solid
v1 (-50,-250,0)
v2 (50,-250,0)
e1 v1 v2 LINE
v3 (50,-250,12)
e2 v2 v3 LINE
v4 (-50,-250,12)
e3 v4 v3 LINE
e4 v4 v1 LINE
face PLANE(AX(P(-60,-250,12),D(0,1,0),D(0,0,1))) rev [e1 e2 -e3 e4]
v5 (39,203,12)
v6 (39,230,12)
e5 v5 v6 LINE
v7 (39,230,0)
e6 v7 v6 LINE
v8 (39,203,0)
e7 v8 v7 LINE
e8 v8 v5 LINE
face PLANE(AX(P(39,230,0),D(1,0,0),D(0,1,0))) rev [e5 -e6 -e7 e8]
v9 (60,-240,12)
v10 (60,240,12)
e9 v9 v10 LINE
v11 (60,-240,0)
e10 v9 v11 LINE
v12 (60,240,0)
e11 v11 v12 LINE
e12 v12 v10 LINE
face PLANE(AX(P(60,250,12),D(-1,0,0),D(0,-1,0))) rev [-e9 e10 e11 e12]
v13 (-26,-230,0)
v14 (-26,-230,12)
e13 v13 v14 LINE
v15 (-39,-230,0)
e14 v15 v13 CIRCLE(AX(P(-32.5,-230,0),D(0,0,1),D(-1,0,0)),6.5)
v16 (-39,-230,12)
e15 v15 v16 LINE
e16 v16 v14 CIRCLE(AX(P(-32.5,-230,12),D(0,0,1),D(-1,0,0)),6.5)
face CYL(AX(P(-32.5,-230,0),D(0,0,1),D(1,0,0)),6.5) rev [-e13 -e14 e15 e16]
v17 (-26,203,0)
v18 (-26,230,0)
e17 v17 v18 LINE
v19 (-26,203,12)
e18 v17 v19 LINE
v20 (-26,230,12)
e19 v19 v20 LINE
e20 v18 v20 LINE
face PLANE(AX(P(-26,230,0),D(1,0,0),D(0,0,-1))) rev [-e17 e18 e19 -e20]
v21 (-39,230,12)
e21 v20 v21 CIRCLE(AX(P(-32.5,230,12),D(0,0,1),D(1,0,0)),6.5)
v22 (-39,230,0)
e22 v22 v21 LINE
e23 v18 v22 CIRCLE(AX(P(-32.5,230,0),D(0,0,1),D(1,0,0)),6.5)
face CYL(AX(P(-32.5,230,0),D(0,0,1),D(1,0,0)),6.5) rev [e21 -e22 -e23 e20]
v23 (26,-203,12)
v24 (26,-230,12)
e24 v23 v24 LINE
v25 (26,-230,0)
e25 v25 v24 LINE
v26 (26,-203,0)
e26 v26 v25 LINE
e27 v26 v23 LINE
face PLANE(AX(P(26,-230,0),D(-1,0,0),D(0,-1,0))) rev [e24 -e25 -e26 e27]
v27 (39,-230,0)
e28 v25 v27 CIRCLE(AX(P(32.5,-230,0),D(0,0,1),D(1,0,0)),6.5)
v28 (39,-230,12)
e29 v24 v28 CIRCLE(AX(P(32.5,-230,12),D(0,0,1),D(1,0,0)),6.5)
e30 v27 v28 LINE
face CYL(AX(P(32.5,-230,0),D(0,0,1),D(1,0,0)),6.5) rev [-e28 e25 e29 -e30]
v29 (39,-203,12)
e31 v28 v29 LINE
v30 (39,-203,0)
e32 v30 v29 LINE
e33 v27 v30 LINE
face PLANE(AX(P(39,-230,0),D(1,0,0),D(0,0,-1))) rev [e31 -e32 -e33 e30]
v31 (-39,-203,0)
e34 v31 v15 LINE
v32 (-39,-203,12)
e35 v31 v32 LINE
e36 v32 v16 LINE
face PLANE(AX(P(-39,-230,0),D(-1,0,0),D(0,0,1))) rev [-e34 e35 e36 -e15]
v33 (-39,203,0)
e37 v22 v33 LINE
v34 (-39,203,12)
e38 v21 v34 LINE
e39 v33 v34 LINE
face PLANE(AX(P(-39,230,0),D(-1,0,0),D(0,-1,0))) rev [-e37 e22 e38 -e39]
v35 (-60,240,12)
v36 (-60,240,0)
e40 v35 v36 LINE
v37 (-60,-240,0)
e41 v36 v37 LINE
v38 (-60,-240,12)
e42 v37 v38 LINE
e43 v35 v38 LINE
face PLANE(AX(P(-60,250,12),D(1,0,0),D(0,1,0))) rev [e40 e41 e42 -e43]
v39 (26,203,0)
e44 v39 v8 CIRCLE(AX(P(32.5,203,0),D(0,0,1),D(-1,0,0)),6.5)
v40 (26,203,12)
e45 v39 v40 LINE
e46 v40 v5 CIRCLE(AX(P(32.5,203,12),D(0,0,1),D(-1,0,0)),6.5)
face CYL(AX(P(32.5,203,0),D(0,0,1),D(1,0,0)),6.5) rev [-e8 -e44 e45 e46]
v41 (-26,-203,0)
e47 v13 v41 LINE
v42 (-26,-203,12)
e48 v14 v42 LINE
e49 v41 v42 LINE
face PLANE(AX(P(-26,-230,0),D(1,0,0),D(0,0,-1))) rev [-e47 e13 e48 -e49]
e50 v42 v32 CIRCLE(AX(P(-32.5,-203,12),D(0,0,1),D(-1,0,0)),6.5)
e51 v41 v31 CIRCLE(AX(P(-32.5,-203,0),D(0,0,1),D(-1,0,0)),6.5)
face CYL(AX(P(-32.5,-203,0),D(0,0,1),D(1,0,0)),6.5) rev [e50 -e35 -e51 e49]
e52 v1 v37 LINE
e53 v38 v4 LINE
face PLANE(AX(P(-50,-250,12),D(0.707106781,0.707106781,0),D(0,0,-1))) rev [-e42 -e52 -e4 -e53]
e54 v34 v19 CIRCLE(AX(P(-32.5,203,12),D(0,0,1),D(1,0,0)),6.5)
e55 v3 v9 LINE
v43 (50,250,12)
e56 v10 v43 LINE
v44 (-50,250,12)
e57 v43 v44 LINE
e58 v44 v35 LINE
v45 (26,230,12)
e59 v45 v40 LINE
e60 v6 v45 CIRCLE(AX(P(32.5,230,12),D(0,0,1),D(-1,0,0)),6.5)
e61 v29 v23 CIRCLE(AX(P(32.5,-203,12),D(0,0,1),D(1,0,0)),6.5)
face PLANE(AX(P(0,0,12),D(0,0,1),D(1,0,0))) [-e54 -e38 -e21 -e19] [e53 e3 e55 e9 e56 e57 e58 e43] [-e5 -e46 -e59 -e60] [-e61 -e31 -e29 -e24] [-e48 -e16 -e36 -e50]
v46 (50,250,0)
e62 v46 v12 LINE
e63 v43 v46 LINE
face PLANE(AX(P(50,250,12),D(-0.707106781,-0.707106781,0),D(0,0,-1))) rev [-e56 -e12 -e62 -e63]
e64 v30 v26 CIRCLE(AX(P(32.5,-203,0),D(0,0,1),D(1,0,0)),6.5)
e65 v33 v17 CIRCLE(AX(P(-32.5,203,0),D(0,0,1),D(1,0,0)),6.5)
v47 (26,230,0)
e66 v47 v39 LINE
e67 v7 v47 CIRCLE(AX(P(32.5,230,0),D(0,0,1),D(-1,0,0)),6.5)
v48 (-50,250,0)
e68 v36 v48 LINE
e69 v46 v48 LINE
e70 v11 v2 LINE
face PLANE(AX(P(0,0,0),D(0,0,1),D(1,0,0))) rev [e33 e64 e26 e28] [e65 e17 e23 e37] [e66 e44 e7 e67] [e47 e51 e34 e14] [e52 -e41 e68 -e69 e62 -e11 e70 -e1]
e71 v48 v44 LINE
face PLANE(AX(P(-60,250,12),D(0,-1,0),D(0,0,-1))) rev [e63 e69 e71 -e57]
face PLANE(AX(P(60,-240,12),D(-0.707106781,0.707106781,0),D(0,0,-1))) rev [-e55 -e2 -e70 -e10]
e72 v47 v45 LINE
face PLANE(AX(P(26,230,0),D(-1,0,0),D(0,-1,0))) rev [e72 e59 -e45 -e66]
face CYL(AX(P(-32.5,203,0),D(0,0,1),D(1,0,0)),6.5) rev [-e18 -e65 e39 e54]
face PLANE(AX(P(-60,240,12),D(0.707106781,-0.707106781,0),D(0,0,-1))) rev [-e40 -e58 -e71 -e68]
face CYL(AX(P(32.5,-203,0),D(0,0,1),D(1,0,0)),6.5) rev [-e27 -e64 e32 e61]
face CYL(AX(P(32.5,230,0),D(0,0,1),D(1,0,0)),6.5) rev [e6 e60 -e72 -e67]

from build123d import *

# Parameters (mm, degrees)
SKETCH1_W           = 120
SKETCH1_H           = 500
BOSS_EXTRUDE1_DEPTH = 12
CUT_EXTRUDE1_DEPTH  = 12
CHAMFER1_SIZE       = 10


with BuildPart() as part:
    # Sketch1 → Boss-Extrude1 (new body)
    with BuildSketch(Plane.XY):
        Rectangle(SKETCH1_W, SKETCH1_H)
    extrude(amount=BOSS_EXTRUDE1_DEPTH)

    # Sketch2 → Cut-Extrude1 (cut)
    with BuildSketch(Plane.XY.offset(12)):
        with BuildLine():
            Line((-26, 230), (-26, 203))
            ThreePointArc((-26, 203), (-32.5, 196.5), (-39, 203))
            Line((-39, 203), (-39, 230))
            ThreePointArc((-39, 230), (-32.5, 236.5), (-26, 230))
        make_face()
        with BuildLine():
            Line((26, 230), (26, 203))
            ThreePointArc((26, 203), (32.5, 196.5), (39, 203))
            Line((39, 203), (39, 230))
            ThreePointArc((39, 230), (32.5, 236.5), (26, 230))
        make_face()
        with BuildLine():
            Line((26, -230), (26, -203))
            ThreePointArc((26, -203), (32.5, -196.5), (39, -203))
            Line((39, -203), (39, -230))
            ThreePointArc((39, -230), (32.5, -236.5), (26, -230))
        make_face()
        with BuildLine():
            Line((-26, -230), (-26, -203))
            ThreePointArc((-26, -203), (-32.5, -196.5), (-39, -203))
            Line((-39, -203), (-39, -230))
            ThreePointArc((-39, -230), (-32.5, -236.5), (-26, -230))
        make_face()
    extrude(amount=-CUT_EXTRUDE1_DEPTH, mode=Mode.SUBTRACT)

    # Chamfer1
    chamfer1_edges = [part.edges().sort_by_distance(p)[0] for p in [
        (60, -250, 6),
        (-60, -250, 6),
        (-60, 250, 6),
        (60, 250, 6),
    ]]
    chamfer(chamfer1_edges, length=CHAMFER1_SIZE)


solid = part.part
